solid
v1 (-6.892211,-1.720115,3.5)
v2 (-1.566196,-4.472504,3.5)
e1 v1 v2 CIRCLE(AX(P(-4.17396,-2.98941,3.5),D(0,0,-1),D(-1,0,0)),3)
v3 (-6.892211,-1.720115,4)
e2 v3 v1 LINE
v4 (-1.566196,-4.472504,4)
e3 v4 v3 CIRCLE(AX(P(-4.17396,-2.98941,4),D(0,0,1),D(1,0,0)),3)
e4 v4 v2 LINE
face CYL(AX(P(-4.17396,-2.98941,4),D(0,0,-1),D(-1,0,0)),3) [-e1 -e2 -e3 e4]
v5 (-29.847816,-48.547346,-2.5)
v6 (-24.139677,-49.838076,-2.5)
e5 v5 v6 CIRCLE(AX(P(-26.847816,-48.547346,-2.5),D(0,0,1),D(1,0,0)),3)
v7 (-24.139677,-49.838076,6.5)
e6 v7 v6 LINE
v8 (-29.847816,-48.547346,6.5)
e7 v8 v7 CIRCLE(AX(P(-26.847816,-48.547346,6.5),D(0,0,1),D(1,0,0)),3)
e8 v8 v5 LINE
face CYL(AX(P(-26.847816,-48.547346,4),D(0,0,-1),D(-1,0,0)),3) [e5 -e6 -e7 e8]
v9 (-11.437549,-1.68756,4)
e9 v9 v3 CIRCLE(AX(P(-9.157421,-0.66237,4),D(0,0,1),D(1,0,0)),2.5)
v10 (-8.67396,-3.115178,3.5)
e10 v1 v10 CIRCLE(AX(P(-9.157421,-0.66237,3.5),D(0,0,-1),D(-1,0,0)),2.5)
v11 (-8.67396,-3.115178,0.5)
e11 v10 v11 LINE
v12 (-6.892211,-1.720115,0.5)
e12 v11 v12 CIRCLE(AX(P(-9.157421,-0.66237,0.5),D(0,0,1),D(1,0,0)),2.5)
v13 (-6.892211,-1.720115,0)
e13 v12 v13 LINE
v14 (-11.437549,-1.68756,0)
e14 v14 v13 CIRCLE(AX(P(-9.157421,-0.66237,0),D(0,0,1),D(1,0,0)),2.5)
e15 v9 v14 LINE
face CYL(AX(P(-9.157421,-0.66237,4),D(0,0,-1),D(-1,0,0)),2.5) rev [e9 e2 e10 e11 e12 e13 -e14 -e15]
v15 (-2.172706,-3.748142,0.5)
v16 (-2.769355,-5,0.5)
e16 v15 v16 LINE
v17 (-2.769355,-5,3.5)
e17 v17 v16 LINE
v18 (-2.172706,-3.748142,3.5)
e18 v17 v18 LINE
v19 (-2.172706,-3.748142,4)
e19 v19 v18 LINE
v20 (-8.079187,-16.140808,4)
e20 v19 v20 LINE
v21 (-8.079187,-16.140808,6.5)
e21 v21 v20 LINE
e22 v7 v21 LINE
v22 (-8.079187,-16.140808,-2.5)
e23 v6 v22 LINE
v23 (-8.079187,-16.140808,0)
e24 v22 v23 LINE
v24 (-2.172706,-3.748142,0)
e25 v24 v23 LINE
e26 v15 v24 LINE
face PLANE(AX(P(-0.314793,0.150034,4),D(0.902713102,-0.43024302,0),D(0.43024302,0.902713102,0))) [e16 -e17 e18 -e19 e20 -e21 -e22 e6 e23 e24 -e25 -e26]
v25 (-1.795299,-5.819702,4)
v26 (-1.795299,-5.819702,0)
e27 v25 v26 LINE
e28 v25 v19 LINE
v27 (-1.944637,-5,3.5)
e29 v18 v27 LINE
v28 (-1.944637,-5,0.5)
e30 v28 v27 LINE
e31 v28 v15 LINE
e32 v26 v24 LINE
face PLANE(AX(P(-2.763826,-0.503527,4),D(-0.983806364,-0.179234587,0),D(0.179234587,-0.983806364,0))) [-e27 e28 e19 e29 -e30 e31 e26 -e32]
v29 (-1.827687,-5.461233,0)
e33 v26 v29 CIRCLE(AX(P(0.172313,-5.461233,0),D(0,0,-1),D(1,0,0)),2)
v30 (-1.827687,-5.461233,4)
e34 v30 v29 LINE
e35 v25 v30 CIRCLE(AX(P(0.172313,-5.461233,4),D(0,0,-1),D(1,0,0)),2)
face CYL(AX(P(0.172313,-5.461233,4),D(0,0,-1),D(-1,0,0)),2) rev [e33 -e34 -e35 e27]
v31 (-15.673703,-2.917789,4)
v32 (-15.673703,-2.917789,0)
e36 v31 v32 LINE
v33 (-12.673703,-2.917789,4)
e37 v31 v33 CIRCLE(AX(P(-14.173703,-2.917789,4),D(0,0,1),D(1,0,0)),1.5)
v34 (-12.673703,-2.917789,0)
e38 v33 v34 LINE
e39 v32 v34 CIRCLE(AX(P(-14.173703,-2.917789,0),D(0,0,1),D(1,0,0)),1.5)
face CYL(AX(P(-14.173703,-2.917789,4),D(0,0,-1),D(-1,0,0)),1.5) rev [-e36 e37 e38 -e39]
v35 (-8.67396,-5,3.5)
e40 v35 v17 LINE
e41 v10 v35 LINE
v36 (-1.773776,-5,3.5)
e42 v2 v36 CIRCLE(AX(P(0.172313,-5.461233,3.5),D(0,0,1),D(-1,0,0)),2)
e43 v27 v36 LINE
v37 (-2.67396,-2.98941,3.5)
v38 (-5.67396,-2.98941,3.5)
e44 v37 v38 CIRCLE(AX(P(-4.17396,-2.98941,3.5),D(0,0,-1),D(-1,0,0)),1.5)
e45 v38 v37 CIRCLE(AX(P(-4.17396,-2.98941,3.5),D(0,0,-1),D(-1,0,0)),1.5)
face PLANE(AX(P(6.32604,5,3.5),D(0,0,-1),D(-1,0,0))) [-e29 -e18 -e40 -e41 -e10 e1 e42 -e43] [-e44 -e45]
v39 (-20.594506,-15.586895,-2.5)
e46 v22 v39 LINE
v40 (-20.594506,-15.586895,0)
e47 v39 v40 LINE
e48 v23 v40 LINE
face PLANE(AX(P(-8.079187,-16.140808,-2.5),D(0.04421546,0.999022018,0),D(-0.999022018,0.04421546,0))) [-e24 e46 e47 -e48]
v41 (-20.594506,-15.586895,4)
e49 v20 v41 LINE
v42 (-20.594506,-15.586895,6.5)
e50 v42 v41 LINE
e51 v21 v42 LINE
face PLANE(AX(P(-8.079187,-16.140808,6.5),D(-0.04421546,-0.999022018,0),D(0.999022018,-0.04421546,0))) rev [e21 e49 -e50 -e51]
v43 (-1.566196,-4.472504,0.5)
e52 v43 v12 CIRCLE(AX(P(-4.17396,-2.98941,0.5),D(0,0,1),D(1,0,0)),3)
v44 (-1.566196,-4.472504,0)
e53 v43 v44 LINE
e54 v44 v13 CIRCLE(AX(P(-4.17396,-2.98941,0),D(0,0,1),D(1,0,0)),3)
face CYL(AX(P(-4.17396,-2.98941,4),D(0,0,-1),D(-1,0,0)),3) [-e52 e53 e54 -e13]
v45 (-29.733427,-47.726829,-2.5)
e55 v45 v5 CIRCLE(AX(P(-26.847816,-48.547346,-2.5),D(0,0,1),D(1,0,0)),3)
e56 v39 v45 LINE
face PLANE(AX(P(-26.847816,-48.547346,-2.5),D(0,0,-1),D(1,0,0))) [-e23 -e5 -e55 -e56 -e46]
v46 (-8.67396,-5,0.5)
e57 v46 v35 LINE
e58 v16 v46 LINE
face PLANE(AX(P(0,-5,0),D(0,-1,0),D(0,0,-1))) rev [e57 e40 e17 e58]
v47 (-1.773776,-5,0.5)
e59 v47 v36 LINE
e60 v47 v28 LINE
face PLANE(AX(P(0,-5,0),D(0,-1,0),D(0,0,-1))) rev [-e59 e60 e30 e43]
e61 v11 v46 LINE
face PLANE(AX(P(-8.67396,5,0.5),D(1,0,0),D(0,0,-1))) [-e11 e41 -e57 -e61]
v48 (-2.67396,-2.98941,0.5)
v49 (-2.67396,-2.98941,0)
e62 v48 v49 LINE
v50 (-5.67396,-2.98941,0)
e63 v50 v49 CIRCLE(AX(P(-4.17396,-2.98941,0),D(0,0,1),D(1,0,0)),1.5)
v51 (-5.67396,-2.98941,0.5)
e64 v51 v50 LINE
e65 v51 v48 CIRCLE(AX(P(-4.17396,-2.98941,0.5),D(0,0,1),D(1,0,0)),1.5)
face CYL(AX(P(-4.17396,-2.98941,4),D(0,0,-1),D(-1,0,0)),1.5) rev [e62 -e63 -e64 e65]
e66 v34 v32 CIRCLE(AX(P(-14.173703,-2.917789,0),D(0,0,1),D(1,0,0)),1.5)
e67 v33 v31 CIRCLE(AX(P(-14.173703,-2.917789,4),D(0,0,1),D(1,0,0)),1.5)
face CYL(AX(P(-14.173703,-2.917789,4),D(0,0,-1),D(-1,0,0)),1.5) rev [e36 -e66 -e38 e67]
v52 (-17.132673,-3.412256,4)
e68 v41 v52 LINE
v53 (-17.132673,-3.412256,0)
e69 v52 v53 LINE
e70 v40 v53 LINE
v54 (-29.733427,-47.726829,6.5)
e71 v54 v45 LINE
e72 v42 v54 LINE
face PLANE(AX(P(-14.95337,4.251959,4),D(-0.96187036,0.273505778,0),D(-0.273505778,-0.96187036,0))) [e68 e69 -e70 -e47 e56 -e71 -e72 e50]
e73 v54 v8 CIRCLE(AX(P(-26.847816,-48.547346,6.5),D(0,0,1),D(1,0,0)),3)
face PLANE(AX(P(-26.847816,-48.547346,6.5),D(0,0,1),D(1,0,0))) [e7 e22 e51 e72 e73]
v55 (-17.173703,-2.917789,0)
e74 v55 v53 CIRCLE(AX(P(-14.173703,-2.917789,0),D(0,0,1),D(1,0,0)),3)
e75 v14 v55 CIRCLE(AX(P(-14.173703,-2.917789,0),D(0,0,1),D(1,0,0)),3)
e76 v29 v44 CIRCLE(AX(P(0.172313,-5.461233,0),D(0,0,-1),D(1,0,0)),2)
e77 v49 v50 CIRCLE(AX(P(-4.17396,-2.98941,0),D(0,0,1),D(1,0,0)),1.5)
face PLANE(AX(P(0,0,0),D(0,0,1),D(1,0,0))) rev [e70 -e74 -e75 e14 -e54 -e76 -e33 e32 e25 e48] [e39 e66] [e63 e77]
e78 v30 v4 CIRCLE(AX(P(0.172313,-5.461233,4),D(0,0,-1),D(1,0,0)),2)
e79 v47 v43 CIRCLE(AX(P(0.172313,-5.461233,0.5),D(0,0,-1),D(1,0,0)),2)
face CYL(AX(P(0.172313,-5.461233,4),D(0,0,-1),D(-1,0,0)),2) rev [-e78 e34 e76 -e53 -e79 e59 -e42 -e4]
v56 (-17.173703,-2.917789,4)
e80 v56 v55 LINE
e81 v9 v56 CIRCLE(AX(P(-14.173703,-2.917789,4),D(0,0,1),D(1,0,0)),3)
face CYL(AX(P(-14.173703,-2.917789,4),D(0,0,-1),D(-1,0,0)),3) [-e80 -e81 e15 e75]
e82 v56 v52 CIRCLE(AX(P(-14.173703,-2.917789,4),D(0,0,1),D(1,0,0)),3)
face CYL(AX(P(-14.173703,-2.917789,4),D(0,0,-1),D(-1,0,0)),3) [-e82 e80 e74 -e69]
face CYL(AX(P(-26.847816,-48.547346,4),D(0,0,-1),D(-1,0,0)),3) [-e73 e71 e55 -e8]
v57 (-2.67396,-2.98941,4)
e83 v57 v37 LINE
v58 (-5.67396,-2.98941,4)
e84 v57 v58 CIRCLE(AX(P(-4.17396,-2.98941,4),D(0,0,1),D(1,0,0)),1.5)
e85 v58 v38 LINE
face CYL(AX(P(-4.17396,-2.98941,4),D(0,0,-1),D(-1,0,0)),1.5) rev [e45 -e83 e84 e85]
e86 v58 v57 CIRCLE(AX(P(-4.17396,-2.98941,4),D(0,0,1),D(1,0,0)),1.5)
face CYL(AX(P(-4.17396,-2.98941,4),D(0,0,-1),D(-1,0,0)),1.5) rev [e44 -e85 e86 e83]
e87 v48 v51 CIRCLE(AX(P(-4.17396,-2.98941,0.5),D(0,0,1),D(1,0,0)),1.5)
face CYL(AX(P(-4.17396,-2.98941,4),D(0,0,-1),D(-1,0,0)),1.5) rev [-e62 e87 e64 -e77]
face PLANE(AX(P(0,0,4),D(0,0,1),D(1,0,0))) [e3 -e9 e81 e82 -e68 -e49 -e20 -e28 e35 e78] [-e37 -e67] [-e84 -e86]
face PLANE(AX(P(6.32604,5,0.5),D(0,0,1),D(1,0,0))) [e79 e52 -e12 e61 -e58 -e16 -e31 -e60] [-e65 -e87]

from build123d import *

# Parameters (mm, degrees)
SKETCH1_R               = 3
BOSS_EXTRUDE1_DEPTH     = 8
CUT_EXTRUDE1_DEPTH      = 10
CUT_EXTRUDE1_DEPTH_BACK = 10
SKETCH2_W               = 30
SKETCH2_H               = 6
BOSS_EXTRUDE2_DEPTH     = 5
SCALE1_SCALE            = 0.5


with BuildPart() as part:
    # Sketch1 → Boss-Extrude1 (new body)
    with BuildSketch(Plane.XY):
        with BuildLine():
            Line((-59.466854234, -95.453658304), (-34.265346163, -6.824512068))
            ThreePointArc((-34.265346163, -6.824512068), (-30.086435736, -0.093123284), (-22.875098798, -3.375120677))
            ThreePointArc((-22.875098798, -3.375120677), (-18.350652777, -6.324611935), (-13.784422872, -3.44023073))
            ThreePointArc((-13.784422872, -3.44023073), (-5.593314668, -0.648514381), (-3.132391837, -8.945007172))
            ThreePointArc((-3.132391837, -8.945007172), (-3.598758132, -10.251856882), (-3.590598772, -11.639404038))
            Line((-3.590598772, -11.639404038), (-4.345412305, -7.496284288))
            Line((-4.345412305, -7.496284288), (-48.279353466, -99.676151096))
            ThreePointArc((-48.279353466, -99.676151096), (-55.814324496, -102.708171614), (-59.466854234, -95.453658304))
        make_face()
        with Locations((-28.347406658, -5.835577277)):
            Circle(SKETCH1_R, mode=Mode.SUBTRACT)
        with Locations((-8.347919622, -5.978819396)):
            Circle(SKETCH1_R, mode=Mode.SUBTRACT)
    extrude(amount=BOSS_EXTRUDE1_DEPTH)

    # Sketch2 → Cut-Extrude1 (cut, two sides: drawn at the far end of the back side and taken through both)
    with BuildSketch(Plane(origin=(0, 0, 0), x_dir=(1, 0, 0), z_dir=(0, 1, 0)).offset(-CUT_EXTRUDE1_DEPTH_BACK)):
        with Locations((-2.347919622, -4)):
            Rectangle(SKETCH2_W, SKETCH2_H)
    extrude(amount=CUT_EXTRUDE1_DEPTH + CUT_EXTRUDE1_DEPTH_BACK, mode=Mode.SUBTRACT)

    # Sketch3 → Boss-Extrude2 (add)
    with BuildSketch(Plane.XY.offset(8)):
        with BuildLine():
            Line((-16.158374435, -32.281615332), (-41.189011455, -31.173790769))
            Line((-41.189011455, -31.173790769), (-59.466854234, -95.453658304))
            ThreePointArc((-59.466854234, -95.453658304), (-55.814324496, -102.708171614), (-48.279353466, -99.676151096))
            Line((-48.279353466, -99.676151096), (-16.158374435, -32.281615332))
        make_face()
    boss_extrude2 = extrude(amount=BOSS_EXTRUDE2_DEPTH)

    # Mirror1: Boss-Extrude2 across plane
    add(boss_extrude2.mirror(Plane.XY.offset(4)))


with BuildPart() as part_1:
    # Scale1: scaled about (0, 0, 0)
    add(part.part.scale(SCALE1_SCALE))


solid = part_1.part
